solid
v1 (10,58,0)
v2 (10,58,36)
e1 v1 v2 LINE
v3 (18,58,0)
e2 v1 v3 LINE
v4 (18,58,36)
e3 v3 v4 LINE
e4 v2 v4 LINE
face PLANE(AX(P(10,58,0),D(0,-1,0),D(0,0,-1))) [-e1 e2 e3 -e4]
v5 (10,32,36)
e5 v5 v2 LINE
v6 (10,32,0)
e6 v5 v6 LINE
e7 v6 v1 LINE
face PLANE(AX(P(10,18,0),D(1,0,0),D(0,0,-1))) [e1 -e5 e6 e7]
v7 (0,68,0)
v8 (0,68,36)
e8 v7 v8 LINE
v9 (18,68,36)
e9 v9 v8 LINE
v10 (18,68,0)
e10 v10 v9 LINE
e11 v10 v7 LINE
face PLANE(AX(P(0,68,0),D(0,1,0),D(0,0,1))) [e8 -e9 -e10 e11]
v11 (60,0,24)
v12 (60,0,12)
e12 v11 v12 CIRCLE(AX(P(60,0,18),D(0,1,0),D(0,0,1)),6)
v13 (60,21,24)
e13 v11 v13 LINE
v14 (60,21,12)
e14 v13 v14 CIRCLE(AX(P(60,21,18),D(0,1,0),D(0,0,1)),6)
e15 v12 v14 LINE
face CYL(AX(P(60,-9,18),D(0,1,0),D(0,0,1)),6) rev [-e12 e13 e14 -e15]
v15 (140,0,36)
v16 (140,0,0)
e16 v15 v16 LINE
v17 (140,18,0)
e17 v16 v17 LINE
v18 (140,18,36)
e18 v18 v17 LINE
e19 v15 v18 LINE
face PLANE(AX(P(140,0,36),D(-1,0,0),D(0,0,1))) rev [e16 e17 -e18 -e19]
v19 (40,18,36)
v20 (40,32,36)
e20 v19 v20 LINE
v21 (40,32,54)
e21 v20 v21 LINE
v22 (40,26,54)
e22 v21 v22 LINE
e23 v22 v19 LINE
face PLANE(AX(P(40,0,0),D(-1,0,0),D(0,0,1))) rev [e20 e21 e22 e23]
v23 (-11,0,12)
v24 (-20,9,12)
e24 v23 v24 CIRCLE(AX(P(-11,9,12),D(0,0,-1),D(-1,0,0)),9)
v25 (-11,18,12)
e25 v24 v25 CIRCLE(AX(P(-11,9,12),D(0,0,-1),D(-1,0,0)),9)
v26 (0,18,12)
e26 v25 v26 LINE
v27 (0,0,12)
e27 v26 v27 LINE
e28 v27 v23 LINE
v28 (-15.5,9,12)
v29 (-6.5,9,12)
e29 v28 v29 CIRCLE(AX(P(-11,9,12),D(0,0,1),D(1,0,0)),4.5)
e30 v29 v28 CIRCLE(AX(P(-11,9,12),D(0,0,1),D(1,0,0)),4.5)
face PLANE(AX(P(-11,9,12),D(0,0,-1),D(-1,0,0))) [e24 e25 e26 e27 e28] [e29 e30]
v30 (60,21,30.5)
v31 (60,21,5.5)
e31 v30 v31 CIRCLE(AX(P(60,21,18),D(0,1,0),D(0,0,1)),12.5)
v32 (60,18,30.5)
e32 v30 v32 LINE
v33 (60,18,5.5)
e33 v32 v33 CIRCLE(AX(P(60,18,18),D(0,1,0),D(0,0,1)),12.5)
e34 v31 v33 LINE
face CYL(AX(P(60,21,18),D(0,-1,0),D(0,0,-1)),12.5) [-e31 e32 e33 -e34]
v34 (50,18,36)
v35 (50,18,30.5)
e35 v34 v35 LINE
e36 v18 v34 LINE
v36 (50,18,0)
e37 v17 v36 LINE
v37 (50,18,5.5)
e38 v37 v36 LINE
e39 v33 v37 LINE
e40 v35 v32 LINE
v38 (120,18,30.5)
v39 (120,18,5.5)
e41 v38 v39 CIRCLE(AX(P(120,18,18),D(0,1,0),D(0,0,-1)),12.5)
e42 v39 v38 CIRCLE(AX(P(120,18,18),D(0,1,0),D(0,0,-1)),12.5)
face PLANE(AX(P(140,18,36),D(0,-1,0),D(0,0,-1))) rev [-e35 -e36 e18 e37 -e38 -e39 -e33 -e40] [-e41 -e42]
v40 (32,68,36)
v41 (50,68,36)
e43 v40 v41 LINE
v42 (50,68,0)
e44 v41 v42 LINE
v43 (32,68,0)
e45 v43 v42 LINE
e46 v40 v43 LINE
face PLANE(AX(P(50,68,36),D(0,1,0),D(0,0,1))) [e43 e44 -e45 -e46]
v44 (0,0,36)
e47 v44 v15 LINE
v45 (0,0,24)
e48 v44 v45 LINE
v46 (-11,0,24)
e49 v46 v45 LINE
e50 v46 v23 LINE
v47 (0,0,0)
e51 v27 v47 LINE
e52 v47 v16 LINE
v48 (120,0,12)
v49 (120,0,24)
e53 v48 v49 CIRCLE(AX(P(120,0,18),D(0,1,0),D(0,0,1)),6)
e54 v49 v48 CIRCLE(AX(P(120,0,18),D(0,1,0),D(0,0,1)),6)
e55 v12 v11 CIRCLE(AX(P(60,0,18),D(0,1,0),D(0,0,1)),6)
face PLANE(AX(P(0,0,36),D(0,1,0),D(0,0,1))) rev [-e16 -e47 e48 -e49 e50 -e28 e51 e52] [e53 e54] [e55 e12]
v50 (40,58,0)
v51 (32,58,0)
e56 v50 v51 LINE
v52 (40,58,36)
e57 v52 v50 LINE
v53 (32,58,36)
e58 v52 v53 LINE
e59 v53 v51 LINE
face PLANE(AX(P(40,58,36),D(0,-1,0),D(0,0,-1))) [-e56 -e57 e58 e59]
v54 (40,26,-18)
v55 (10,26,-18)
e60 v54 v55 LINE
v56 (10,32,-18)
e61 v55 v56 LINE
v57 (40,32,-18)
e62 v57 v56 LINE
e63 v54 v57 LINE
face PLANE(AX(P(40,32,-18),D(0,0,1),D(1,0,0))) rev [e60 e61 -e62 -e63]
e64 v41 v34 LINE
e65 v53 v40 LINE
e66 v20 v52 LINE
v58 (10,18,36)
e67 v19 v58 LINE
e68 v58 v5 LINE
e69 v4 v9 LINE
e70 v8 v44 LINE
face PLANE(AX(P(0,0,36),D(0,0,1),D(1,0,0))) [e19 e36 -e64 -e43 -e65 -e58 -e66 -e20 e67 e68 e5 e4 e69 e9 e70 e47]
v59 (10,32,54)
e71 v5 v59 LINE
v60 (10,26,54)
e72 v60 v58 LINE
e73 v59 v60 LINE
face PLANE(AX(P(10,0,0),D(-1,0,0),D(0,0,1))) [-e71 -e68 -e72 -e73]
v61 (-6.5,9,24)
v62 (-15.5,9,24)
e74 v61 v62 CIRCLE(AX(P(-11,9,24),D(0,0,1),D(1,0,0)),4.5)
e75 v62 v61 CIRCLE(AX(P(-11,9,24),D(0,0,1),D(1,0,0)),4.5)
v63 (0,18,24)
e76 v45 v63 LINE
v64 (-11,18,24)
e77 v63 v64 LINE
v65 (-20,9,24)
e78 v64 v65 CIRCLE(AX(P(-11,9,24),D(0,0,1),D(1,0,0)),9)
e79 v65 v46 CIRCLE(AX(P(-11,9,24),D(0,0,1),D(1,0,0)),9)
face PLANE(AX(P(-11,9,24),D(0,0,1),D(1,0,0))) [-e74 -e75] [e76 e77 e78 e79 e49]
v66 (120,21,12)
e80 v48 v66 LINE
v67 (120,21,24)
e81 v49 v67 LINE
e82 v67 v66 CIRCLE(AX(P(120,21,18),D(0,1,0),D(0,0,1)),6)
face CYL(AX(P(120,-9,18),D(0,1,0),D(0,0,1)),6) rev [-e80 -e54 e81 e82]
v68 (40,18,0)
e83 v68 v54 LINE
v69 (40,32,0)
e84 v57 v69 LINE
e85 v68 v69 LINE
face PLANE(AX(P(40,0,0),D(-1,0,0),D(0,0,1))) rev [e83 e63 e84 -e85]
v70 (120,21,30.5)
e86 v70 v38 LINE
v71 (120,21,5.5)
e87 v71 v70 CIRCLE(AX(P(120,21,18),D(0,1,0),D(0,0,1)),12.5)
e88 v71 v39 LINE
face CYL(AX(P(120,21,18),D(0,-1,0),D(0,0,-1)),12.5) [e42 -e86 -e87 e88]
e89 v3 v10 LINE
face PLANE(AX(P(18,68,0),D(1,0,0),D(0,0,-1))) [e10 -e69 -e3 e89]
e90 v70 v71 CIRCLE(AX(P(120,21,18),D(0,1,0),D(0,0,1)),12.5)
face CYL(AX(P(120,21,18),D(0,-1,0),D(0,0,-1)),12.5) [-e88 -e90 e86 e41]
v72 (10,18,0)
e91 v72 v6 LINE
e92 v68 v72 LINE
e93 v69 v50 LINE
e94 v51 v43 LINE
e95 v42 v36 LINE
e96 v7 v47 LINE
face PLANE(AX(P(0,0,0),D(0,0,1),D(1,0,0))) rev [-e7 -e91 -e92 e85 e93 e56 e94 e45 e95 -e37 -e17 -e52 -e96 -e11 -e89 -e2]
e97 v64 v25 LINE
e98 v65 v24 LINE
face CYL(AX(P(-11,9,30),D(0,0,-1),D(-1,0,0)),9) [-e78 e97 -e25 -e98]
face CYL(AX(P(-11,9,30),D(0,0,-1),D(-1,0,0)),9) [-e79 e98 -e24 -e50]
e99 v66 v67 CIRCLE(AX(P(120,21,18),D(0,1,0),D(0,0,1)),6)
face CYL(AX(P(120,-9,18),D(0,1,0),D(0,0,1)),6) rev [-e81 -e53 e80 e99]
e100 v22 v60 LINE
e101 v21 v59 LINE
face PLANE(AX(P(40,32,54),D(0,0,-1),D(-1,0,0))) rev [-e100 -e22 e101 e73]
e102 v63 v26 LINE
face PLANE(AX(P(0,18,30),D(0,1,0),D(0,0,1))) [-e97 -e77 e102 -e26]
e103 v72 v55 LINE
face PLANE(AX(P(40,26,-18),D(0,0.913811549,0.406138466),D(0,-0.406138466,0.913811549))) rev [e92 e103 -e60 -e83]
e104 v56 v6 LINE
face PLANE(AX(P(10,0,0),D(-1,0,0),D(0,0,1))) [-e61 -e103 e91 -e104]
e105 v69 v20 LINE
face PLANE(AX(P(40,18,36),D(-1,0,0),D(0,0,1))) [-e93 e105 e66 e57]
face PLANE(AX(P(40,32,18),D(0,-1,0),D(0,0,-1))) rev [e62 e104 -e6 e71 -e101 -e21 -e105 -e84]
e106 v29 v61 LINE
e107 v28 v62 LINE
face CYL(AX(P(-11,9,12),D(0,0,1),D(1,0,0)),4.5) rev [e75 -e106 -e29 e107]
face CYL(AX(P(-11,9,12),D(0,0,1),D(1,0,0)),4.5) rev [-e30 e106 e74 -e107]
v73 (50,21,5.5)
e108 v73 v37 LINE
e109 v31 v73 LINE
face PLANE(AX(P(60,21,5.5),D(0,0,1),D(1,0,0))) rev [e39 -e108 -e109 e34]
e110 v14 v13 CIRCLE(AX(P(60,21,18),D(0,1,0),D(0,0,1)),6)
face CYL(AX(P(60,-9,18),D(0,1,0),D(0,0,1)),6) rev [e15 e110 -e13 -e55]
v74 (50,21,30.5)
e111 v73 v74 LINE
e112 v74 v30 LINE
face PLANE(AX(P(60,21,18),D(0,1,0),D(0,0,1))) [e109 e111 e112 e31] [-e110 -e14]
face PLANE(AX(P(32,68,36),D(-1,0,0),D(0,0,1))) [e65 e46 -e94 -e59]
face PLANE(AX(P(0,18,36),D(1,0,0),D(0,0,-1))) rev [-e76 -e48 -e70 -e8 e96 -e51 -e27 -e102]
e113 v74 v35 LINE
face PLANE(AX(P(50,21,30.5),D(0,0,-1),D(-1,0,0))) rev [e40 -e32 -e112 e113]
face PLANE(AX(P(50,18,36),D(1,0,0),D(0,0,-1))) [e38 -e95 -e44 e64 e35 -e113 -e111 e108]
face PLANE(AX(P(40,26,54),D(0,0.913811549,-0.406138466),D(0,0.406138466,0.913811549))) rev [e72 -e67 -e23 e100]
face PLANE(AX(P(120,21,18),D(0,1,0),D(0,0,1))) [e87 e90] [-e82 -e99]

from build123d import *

# Parameters (mm, degrees)
BASE_PROFILE_SKETCH_W      = 140
BASE_PROFILE_SKETCH_H      = 18
BASE_BLOCK_DEPTH           = 36
UPRIGHT_BLOCK_DEPTH        = 36
GUIDE_RAIL_BOSS_DEPTH      = 30
GUIDE_CAP_BOSS_DEPTH       = 36
SIDE_LUG_DEPTH             = 30
LUG_POCKET_18_DEPTH        = 12
LUG_START                  = -6
LUG_RECESS_18_DEPTH        = 6
LUG_HOLE_SKETCH_R          = 4.5
LUG_HOLE_9_DEPTH           = 12
MOUNTING_PAD_1_25_DEPTH    = 3
MOUNTING_PAD_2_SKETCH_R    = 12.5
MOUNTING_PAD_2_25_DEPTH    = 3
MOUNTING_HOLES_SKETCH_R    = 6
MOUNTING_HOLES_2X_12_DEPTH = 30


with BuildPart() as part:
    # Base Profile Sketch → Base Block (new body)
    with BuildSketch(Plane.XY):
        with Locations((70, 9)):
            Rectangle(BASE_PROFILE_SKETCH_W, BASE_PROFILE_SKETCH_H)
    extrude(amount=BASE_BLOCK_DEPTH)

    # Upright Profile Sketch → Upright Block (add)
    with BuildSketch(Plane.XY.offset(36)):
        Polygon((0, 18), (0, 68), (18, 68), (18, 58), (10, 58), (10, 18), align=None)
    extrude(amount=-UPRIGHT_BLOCK_DEPTH)

    # Guide Rail Sketch → Guide Rail Boss (add)
    with BuildSketch(Plane(origin=(10, 0, 0), x_dir=(0, 0, -1), z_dir=(1, 0, 0))):
        Polygon((-18, 32), (18, 32), (18, 26), (0, 18), (-18, 18), (-36, 18), (-54, 26), (-54, 32), align=None)
    extrude(amount=GUIDE_RAIL_BOSS_DEPTH)

    # Guide Cap Sketch → Guide Cap Boss (add)
    with BuildSketch(Plane(origin=(0, 0, 0), x_dir=(-1, 0, 0), z_dir=(0, 0, -1))):
        Polygon((-40, 18), (-50, 18), (-50, 68), (-32, 68), (-32, 58), (-40, 58), align=None)
    extrude(amount=-GUIDE_CAP_BOSS_DEPTH)

    # Side Lug Sketch → Side Lug (add)
    with BuildSketch(Plane(origin=(0, 0, 0), x_dir=(-1, 0, 0), z_dir=(0, 0, -1))):
        with BuildLine():
            Line((0, 0), (0, 18))
            Line((0, 18), (10, 18))
            Line((10, 18), (11, 18))
            ThreePointArc((11, 18), (20, 9), (11, 0))
            Line((11, 0), (0, 0))
        make_face()
    extrude(amount=-SIDE_LUG_DEPTH)

    # Lug Pocket Sketch → Lug Pocket Ø18 (cut)
    with BuildSketch(Plane(origin=(0, 0, 0), x_dir=(-1, 0, 0), z_dir=(0, 0, -1))):
        with BuildLine():
            Line((0, 18), (11, 18))
            ThreePointArc((11, 18), (20, 9), (11, 0))
            Line((11, 0), (0, 0))
            Line((0, 0), (0, 18))
        make_face()
    extrude(amount=-LUG_POCKET_18_DEPTH, mode=Mode.SUBTRACT)

    # Lug Recess Sketch → Lug Recess Ø18 (cut)
    with BuildSketch(Plane.XY.offset(30).offset(LUG_START)):
        with BuildLine():
            Line((0, 18), (-11, 18))
            ThreePointArc((-11, 18), (-20, 9), (-11, 0))
            Line((-11, 0), (0, 0))
            Line((0, 0), (0, 18))
        make_face()
    extrude(amount=LUG_RECESS_18_DEPTH, mode=Mode.SUBTRACT)

    # Lug Hole Sketch → Lug Hole Ø9 (cut)
    with BuildSketch(Plane.XY.offset(24)):
        with Locations((-11, 9)):
            Circle(LUG_HOLE_SKETCH_R)
    extrude(amount=-LUG_HOLE_9_DEPTH, mode=Mode.SUBTRACT)

    # Mounting Pad 1 Sketch → Mounting Pad 1 Ø25 (add)
    with BuildSketch(Plane(origin=(0, 18, 0), x_dir=(1, 0, 0), z_dir=(0, 1, 0))):
        with BuildLine():
            Line((60, -5.5), (50, -5.5))
            Line((50, -5.5), (50, -30.5))
            Line((50, -30.5), (60, -30.5))
            ThreePointArc((60, -30.5), (72.5, -18), (60, -5.5))
        make_face()
    extrude(amount=MOUNTING_PAD_1_25_DEPTH)

    # Mounting Pad 2 Sketch → Mounting Pad 2 Ø25 (add)
    with BuildSketch(Plane(origin=(0, 18, 0), x_dir=(1, 0, 0), z_dir=(0, 1, 0))):
        with Locations(Location((120, -18, 0), (0, 0, 90))):
            Circle(MOUNTING_PAD_2_SKETCH_R)
    extrude(amount=MOUNTING_PAD_2_25_DEPTH)

    # Mounting Holes Sketch → Mounting Holes 2xØ12 (cut)
    with BuildSketch(Plane(origin=(0, 21, 0), x_dir=(1, 0, 0), z_dir=(0, 1, 0))):
        with Locations(Location((120, -18, 0), (0, 0, 270))):
            Circle(MOUNTING_HOLES_SKETCH_R)
        with Locations(Location((60, -18, 0), (0, 0, 270))):
            Circle(MOUNTING_HOLES_SKETCH_R)
    extrude(amount=-MOUNTING_HOLES_2X_12_DEPTH, mode=Mode.SUBTRACT)


solid = part.part
